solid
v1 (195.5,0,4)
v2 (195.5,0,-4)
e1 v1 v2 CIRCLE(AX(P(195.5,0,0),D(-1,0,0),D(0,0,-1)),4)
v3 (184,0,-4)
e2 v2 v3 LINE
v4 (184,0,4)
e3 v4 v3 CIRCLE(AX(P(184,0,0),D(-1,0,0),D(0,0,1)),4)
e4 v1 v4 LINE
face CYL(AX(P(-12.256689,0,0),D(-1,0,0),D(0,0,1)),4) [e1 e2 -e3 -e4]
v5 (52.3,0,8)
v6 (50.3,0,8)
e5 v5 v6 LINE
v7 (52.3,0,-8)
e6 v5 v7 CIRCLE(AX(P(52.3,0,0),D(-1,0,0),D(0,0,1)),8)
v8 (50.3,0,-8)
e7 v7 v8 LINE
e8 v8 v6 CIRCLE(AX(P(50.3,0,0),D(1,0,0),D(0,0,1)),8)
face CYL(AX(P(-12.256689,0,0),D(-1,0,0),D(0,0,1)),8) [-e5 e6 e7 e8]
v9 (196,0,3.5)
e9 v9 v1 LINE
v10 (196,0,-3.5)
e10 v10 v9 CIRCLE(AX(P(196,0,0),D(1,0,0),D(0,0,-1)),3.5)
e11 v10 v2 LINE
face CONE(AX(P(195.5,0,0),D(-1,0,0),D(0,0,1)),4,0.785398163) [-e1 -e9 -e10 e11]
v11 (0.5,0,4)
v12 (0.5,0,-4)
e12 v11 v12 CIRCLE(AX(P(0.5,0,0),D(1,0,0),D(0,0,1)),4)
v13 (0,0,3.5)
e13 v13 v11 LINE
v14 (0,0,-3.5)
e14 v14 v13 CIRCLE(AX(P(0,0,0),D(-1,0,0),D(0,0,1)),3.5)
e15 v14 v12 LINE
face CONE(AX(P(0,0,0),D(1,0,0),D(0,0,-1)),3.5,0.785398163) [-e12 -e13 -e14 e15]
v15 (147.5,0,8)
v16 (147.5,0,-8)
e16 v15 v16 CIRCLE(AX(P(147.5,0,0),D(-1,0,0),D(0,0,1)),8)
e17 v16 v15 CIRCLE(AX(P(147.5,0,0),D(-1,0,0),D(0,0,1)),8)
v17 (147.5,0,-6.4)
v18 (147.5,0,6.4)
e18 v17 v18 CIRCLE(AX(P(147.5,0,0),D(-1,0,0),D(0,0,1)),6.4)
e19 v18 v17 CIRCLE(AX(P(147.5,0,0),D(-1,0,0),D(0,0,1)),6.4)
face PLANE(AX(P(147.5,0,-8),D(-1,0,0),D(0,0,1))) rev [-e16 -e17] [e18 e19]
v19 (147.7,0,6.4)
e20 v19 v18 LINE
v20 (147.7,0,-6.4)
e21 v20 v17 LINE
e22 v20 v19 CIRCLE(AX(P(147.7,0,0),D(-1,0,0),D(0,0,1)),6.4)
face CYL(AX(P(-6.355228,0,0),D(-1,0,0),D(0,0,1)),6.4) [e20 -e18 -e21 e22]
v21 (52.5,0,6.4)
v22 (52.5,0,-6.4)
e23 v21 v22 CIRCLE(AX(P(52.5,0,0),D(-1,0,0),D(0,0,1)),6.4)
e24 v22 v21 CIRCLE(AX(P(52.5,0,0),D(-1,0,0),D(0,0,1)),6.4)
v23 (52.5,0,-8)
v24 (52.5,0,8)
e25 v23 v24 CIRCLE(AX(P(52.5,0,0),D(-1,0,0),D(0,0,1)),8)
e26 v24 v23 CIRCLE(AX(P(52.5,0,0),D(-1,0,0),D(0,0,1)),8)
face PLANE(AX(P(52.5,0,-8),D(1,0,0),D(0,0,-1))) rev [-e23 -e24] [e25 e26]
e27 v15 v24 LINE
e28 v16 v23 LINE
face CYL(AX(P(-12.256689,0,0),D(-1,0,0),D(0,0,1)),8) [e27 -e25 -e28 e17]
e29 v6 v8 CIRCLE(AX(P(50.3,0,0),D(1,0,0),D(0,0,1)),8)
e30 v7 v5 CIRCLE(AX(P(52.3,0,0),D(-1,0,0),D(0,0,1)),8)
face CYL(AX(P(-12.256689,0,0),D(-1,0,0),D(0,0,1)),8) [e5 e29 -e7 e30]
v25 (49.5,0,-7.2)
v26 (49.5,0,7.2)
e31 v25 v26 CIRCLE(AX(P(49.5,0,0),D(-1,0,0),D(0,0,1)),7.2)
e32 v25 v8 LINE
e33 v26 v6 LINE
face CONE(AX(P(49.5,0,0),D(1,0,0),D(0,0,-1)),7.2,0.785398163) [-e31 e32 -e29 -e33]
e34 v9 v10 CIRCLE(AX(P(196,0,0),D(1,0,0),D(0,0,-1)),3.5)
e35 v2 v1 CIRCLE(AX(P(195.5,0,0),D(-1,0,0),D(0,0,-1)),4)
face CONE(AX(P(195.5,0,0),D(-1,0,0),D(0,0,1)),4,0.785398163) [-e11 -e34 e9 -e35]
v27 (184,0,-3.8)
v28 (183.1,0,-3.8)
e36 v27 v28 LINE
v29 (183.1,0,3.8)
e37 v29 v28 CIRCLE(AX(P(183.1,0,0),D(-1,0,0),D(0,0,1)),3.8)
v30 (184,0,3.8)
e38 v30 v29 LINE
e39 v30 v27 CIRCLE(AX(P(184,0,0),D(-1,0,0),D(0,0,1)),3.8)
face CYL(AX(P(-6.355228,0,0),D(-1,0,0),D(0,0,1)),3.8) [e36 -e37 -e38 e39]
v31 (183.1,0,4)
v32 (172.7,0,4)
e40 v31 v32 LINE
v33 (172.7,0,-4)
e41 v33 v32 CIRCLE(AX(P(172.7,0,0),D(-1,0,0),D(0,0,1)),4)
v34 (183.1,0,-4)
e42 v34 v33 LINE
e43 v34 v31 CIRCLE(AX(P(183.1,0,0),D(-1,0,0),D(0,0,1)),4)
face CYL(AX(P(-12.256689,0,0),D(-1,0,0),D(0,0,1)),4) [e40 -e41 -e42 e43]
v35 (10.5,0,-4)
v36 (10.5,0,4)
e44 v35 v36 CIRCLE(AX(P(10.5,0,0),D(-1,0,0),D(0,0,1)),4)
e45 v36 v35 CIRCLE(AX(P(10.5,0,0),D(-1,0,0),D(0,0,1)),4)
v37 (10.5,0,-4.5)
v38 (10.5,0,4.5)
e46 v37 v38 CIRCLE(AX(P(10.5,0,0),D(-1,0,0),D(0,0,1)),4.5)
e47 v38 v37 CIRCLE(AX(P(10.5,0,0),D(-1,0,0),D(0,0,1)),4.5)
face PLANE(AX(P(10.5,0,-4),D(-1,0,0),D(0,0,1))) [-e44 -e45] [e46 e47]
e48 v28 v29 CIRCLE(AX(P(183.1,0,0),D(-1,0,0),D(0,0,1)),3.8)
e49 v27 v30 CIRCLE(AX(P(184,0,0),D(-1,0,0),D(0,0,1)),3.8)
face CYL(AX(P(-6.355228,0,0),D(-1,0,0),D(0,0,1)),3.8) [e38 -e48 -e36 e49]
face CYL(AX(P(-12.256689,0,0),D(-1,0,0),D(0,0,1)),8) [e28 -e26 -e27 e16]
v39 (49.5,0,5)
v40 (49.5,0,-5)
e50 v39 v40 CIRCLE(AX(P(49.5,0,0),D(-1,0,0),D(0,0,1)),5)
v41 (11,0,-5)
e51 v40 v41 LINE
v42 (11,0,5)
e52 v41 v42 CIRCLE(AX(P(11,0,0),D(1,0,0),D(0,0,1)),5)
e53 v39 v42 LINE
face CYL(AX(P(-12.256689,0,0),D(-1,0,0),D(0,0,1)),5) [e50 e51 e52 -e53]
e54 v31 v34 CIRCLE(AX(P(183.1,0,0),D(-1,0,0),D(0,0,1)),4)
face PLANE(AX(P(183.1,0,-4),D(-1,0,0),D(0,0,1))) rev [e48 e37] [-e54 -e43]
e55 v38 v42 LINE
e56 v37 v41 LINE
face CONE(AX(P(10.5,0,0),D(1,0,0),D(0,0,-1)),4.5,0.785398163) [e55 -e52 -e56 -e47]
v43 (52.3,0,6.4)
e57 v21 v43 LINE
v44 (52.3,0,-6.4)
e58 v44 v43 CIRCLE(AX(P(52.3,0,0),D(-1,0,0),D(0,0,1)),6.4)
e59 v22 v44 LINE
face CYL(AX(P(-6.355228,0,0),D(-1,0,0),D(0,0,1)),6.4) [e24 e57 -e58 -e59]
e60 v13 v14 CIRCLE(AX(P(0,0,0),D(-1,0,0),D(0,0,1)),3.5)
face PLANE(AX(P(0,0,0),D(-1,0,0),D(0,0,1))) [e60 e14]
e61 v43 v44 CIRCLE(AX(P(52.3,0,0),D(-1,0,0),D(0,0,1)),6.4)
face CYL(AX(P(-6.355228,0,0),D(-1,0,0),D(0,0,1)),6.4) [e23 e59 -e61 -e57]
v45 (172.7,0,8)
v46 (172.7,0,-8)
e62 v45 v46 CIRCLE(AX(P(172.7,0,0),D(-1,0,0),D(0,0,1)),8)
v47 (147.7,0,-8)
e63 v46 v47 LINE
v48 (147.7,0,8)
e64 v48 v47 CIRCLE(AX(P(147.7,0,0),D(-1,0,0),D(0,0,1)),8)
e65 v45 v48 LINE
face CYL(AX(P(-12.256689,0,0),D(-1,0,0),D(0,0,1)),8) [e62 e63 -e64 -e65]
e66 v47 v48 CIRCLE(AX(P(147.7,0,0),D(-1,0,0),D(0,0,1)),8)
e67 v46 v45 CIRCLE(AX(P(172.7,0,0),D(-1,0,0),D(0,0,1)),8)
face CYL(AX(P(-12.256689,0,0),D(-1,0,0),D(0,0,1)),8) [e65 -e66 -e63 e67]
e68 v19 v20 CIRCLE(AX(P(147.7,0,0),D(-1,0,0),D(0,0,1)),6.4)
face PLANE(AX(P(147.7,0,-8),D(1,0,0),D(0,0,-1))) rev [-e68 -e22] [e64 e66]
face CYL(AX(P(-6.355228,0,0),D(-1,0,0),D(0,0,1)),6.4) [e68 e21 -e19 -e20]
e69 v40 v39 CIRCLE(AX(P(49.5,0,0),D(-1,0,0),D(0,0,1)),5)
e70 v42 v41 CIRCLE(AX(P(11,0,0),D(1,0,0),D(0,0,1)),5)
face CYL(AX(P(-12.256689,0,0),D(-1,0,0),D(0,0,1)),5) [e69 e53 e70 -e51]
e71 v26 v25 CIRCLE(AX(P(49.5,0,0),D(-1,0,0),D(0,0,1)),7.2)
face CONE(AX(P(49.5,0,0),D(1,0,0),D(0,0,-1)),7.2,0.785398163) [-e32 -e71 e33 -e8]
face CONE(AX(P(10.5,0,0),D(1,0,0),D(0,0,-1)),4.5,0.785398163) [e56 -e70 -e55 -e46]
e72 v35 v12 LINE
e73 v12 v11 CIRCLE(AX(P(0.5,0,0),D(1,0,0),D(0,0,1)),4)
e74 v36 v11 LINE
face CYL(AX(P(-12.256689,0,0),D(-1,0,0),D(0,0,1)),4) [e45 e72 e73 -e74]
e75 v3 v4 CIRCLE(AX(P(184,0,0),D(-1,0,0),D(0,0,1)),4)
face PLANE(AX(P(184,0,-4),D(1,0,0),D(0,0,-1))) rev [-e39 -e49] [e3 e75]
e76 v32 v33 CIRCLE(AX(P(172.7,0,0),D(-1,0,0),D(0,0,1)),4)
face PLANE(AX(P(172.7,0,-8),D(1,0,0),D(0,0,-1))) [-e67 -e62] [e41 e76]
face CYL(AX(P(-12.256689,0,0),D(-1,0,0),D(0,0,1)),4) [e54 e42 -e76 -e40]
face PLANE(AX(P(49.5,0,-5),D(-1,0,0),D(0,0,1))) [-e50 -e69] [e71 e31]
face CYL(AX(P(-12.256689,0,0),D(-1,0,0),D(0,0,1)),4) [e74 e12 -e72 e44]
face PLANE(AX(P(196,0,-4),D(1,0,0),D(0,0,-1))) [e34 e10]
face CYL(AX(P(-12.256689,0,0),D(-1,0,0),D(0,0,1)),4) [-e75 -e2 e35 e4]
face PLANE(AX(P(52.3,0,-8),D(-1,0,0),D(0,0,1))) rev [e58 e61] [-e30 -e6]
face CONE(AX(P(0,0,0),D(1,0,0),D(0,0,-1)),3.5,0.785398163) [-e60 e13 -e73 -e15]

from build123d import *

# Parameters (mm, degrees)
SKETCH2_W     = 0.2
SKETCH2_H     = 1.6
SKETCH2_W_2   = 0.9
SKETCH2_H_2   = 0.2
CHAMFER1_SIZE = 0.5
CHAMFER2_SIZE = 0.8


with BuildPart() as part:
    # Sketch1 → Revolve1 (revolve)
    with BuildSketch(Plane(origin=(0, 0, 0), x_dir=(1, 0, 0), z_dir=(0, 1, 0))):
        Polygon((0, 0), (0, -4), (10.5, -4), (10.5, -5), (49.5, -5), (49.5, -8), (172.7, -8), (172.7, -4), (196, -4), (196, 0), align=None)
    revolve(axis=Axis((-12.256689328, 0, 0), (1, 0, 0)))

    # Sketch2 → Cut-Revolve1 (revolve, cut)
    with BuildSketch(Plane(origin=(0, 0, 0), x_dir=(1, 0, 0), z_dir=(0, 1, 0))):
        with Locations((52.4, -7.2)):
            Rectangle(SKETCH2_W, SKETCH2_H)
        with Locations((147.6, -7.2)):
            Rectangle(SKETCH2_W, SKETCH2_H)
        with Locations((183.55, -3.9)):
            Rectangle(SKETCH2_W_2, SKETCH2_H_2)
    revolve(axis=Axis((-6.355227553, 0, 0), (1, 0, 0)), mode=Mode.SUBTRACT)

    # Chamfer1
    chamfer1_edges = [part.edges().sort_by_distance(p)[0] for p in [
        (0, 0, -4),
        (196, 0, -4),
        (10.5, 0, -5),
    ]]
    chamfer(chamfer1_edges, length=CHAMFER1_SIZE)

    # Chamfer2
    chamfer2_edges = [part.edges().sort_by_distance(p)[0] for p in [
        (49.5, 0, -8),
    ]]
    chamfer(chamfer2_edges, length=CHAMFER2_SIZE)


solid = part.part
